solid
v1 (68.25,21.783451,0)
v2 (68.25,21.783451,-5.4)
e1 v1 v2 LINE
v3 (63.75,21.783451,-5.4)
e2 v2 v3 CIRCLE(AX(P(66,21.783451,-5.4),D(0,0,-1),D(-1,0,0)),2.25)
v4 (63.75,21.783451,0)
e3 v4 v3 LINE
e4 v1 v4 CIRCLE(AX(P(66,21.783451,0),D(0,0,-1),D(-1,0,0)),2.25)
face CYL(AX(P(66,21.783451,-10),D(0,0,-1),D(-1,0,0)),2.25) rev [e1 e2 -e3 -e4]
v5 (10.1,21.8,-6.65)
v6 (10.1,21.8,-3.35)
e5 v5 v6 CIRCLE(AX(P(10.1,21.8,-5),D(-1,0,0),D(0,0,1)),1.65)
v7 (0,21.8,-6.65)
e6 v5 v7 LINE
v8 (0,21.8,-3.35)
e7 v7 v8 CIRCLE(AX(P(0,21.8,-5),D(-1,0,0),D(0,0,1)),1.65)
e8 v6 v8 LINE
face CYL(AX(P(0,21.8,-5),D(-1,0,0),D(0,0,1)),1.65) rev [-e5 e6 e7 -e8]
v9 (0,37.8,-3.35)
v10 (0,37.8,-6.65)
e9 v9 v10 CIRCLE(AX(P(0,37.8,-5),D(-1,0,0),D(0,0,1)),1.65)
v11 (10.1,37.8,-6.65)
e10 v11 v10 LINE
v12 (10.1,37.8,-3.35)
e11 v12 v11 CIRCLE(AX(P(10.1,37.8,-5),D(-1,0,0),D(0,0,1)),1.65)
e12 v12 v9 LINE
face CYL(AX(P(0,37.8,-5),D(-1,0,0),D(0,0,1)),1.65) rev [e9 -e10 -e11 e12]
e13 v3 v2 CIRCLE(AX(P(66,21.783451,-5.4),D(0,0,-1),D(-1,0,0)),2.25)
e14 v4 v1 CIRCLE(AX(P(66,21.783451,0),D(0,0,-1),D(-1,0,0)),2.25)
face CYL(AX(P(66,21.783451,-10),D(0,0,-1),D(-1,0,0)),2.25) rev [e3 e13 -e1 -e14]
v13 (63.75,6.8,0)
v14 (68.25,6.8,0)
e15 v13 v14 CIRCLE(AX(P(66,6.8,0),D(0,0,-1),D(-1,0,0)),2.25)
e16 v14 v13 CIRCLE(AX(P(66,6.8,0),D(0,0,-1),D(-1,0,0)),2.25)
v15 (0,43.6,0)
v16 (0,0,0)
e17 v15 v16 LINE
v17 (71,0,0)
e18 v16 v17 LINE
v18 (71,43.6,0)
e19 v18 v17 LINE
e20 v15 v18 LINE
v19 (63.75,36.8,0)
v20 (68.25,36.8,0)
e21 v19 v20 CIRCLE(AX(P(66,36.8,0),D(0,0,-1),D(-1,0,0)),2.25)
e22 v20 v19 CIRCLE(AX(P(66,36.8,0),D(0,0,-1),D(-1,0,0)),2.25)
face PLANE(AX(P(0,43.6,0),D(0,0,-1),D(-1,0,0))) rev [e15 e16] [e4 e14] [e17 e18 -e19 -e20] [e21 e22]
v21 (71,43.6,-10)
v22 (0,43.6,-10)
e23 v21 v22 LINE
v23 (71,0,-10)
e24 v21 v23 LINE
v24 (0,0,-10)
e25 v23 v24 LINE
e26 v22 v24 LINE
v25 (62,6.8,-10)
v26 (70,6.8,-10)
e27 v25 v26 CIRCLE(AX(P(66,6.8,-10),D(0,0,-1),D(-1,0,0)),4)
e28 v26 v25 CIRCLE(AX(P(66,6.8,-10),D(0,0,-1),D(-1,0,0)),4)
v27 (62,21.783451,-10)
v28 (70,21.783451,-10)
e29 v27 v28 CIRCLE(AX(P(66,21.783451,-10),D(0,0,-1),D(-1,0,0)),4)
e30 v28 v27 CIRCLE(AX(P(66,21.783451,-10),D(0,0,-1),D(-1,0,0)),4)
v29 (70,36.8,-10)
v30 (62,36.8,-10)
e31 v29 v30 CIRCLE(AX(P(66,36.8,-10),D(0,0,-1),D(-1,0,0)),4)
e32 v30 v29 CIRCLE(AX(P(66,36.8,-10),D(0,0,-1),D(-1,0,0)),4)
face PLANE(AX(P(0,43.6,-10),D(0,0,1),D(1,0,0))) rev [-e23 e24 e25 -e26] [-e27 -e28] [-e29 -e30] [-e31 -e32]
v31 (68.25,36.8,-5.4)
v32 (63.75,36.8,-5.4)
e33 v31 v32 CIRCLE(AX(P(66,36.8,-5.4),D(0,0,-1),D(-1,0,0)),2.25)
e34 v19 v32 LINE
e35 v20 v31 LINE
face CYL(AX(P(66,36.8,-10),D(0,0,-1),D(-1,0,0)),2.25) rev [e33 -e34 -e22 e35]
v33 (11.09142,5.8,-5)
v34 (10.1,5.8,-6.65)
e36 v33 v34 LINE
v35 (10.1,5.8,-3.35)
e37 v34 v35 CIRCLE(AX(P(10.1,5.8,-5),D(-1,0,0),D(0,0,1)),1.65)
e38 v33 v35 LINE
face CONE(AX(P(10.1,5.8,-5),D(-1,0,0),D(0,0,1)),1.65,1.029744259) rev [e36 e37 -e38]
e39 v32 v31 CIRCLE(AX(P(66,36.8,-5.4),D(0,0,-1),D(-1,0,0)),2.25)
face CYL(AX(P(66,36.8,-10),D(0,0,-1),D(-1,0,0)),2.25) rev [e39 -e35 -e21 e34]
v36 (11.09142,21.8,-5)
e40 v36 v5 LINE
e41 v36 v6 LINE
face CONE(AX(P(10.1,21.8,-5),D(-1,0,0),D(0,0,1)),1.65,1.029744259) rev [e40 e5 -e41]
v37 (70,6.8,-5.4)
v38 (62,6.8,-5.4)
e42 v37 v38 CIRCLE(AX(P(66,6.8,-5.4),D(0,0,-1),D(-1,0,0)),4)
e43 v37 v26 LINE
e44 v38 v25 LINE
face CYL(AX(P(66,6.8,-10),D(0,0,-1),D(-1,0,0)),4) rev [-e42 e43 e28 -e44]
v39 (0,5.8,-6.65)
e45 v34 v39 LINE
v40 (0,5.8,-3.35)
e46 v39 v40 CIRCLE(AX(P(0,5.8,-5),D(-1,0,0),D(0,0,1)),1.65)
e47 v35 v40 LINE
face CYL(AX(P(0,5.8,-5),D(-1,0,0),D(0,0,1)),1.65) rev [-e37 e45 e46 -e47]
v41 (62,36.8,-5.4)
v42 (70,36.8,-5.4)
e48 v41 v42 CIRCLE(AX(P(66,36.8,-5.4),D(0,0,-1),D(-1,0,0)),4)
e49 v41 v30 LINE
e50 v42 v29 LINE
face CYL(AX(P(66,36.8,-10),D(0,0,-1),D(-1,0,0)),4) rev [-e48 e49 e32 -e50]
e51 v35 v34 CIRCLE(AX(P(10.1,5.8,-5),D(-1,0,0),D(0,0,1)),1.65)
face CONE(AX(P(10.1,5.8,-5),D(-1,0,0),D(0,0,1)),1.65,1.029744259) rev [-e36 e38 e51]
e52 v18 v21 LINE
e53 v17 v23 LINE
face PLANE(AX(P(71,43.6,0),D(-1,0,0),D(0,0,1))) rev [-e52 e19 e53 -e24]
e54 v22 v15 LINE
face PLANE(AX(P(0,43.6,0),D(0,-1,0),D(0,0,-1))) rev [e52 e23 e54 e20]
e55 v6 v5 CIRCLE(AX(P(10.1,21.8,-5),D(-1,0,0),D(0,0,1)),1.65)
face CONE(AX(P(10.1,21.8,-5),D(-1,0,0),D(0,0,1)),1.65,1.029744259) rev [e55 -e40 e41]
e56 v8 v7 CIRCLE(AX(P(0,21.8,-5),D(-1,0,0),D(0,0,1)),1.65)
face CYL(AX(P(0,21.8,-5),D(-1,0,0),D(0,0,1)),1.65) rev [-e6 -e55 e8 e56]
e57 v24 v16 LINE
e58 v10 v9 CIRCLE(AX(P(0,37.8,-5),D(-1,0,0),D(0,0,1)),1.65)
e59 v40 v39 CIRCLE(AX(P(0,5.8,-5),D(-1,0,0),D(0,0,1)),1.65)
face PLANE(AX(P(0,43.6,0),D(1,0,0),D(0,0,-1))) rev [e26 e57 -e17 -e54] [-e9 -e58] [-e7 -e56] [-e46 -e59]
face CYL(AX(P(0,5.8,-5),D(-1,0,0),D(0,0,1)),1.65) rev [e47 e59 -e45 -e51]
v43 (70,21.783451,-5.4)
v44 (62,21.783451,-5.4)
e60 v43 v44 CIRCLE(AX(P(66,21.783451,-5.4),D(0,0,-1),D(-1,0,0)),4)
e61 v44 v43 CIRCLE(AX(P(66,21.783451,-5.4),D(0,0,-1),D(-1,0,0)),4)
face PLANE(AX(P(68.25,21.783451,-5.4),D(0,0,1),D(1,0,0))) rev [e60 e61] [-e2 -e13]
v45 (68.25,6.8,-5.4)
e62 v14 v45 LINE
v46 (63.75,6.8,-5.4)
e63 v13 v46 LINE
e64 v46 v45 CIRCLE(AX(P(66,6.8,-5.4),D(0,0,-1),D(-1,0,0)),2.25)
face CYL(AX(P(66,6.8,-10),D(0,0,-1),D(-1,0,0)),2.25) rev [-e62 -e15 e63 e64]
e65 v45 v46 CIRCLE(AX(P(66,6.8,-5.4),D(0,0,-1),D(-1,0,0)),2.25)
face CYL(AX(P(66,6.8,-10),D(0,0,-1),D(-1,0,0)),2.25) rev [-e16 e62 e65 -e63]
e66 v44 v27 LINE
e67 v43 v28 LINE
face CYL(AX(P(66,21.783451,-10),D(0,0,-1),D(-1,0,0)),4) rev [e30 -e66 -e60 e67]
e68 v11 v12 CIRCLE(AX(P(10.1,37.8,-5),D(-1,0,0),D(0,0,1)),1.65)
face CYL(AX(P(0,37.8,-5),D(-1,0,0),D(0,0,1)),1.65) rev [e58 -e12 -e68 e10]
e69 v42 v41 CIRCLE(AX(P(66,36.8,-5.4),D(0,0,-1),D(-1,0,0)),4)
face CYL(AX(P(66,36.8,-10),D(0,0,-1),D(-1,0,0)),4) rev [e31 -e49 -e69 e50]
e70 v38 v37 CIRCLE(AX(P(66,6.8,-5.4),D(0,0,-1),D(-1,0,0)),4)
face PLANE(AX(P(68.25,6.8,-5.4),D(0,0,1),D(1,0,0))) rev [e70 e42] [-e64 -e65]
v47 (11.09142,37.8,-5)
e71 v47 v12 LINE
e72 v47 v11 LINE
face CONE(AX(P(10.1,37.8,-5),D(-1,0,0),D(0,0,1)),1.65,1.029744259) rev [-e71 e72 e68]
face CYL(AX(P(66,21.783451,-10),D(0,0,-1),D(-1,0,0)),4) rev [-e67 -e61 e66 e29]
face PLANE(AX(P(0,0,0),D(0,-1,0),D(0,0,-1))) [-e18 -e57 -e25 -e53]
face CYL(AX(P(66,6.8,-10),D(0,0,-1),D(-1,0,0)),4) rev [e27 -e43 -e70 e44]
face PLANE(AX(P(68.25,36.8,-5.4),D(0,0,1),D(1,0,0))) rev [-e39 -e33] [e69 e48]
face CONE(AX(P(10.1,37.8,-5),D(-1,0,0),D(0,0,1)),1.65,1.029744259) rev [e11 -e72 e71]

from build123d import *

# Parameters (mm, degrees)
SKETCH_1_W                   = 71
SKETCH_1_H                   = 10
EXTRUDE_1_DEPTH              = 43.6
HOLE_WIZARD_M4_1_D           = 4.5
HOLE_WIZARD_M4_1_CBORE_D     = 8
HOLE_WIZARD_M4_1_CBORE_DEPTH = 4.6
HOLE_WIZARD_M4_1_2_D         = 3.3
HOLE_WIZARD_M4_1_2_DEPTH     = 10.1
HOLE_WIZARD_M4_1_2_TIP       = 0.991420021


with BuildPart() as part:
    # 草图1 → 凸台-拉伸1 (new body)
    with BuildSketch(Plane(origin=(0, 0, 0), x_dir=(1, 0, 0), z_dir=(0, 1, 0))):
        with Locations((35.5, 5)):
            Rectangle(SKETCH_1_W, SKETCH_1_H)
    extrude(amount=EXTRUDE_1_DEPTH)

    # Hole Wizard M4 _1 (through all)
    with Locations(Plane(origin=(0, 0, -10), x_dir=(-1, 0, 0), z_dir=(0, 0, -1))):
        with Locations((-66, 36.8), (-66, 21.783451384), (-66, 6.8)):
            CounterBoreHole(HOLE_WIZARD_M4_1_D / 2, HOLE_WIZARD_M4_1_CBORE_D / 2, HOLE_WIZARD_M4_1_CBORE_DEPTH)

    # Hole Wizard M4 _1 2
    with Locations(Plane.ZY):
        with Locations((-5, 37.8), (-5, 21.8), (-5, 5.8)):
            Hole(HOLE_WIZARD_M4_1_2_D / 2, depth=HOLE_WIZARD_M4_1_2_DEPTH)
            with Locations((0, 0, -(HOLE_WIZARD_M4_1_2_DEPTH + HOLE_WIZARD_M4_1_2_TIP / 2))):  # 118° drill point
                Cone(0, HOLE_WIZARD_M4_1_2_D / 2, HOLE_WIZARD_M4_1_2_TIP, mode=Mode.SUBTRACT)


solid = part.part
